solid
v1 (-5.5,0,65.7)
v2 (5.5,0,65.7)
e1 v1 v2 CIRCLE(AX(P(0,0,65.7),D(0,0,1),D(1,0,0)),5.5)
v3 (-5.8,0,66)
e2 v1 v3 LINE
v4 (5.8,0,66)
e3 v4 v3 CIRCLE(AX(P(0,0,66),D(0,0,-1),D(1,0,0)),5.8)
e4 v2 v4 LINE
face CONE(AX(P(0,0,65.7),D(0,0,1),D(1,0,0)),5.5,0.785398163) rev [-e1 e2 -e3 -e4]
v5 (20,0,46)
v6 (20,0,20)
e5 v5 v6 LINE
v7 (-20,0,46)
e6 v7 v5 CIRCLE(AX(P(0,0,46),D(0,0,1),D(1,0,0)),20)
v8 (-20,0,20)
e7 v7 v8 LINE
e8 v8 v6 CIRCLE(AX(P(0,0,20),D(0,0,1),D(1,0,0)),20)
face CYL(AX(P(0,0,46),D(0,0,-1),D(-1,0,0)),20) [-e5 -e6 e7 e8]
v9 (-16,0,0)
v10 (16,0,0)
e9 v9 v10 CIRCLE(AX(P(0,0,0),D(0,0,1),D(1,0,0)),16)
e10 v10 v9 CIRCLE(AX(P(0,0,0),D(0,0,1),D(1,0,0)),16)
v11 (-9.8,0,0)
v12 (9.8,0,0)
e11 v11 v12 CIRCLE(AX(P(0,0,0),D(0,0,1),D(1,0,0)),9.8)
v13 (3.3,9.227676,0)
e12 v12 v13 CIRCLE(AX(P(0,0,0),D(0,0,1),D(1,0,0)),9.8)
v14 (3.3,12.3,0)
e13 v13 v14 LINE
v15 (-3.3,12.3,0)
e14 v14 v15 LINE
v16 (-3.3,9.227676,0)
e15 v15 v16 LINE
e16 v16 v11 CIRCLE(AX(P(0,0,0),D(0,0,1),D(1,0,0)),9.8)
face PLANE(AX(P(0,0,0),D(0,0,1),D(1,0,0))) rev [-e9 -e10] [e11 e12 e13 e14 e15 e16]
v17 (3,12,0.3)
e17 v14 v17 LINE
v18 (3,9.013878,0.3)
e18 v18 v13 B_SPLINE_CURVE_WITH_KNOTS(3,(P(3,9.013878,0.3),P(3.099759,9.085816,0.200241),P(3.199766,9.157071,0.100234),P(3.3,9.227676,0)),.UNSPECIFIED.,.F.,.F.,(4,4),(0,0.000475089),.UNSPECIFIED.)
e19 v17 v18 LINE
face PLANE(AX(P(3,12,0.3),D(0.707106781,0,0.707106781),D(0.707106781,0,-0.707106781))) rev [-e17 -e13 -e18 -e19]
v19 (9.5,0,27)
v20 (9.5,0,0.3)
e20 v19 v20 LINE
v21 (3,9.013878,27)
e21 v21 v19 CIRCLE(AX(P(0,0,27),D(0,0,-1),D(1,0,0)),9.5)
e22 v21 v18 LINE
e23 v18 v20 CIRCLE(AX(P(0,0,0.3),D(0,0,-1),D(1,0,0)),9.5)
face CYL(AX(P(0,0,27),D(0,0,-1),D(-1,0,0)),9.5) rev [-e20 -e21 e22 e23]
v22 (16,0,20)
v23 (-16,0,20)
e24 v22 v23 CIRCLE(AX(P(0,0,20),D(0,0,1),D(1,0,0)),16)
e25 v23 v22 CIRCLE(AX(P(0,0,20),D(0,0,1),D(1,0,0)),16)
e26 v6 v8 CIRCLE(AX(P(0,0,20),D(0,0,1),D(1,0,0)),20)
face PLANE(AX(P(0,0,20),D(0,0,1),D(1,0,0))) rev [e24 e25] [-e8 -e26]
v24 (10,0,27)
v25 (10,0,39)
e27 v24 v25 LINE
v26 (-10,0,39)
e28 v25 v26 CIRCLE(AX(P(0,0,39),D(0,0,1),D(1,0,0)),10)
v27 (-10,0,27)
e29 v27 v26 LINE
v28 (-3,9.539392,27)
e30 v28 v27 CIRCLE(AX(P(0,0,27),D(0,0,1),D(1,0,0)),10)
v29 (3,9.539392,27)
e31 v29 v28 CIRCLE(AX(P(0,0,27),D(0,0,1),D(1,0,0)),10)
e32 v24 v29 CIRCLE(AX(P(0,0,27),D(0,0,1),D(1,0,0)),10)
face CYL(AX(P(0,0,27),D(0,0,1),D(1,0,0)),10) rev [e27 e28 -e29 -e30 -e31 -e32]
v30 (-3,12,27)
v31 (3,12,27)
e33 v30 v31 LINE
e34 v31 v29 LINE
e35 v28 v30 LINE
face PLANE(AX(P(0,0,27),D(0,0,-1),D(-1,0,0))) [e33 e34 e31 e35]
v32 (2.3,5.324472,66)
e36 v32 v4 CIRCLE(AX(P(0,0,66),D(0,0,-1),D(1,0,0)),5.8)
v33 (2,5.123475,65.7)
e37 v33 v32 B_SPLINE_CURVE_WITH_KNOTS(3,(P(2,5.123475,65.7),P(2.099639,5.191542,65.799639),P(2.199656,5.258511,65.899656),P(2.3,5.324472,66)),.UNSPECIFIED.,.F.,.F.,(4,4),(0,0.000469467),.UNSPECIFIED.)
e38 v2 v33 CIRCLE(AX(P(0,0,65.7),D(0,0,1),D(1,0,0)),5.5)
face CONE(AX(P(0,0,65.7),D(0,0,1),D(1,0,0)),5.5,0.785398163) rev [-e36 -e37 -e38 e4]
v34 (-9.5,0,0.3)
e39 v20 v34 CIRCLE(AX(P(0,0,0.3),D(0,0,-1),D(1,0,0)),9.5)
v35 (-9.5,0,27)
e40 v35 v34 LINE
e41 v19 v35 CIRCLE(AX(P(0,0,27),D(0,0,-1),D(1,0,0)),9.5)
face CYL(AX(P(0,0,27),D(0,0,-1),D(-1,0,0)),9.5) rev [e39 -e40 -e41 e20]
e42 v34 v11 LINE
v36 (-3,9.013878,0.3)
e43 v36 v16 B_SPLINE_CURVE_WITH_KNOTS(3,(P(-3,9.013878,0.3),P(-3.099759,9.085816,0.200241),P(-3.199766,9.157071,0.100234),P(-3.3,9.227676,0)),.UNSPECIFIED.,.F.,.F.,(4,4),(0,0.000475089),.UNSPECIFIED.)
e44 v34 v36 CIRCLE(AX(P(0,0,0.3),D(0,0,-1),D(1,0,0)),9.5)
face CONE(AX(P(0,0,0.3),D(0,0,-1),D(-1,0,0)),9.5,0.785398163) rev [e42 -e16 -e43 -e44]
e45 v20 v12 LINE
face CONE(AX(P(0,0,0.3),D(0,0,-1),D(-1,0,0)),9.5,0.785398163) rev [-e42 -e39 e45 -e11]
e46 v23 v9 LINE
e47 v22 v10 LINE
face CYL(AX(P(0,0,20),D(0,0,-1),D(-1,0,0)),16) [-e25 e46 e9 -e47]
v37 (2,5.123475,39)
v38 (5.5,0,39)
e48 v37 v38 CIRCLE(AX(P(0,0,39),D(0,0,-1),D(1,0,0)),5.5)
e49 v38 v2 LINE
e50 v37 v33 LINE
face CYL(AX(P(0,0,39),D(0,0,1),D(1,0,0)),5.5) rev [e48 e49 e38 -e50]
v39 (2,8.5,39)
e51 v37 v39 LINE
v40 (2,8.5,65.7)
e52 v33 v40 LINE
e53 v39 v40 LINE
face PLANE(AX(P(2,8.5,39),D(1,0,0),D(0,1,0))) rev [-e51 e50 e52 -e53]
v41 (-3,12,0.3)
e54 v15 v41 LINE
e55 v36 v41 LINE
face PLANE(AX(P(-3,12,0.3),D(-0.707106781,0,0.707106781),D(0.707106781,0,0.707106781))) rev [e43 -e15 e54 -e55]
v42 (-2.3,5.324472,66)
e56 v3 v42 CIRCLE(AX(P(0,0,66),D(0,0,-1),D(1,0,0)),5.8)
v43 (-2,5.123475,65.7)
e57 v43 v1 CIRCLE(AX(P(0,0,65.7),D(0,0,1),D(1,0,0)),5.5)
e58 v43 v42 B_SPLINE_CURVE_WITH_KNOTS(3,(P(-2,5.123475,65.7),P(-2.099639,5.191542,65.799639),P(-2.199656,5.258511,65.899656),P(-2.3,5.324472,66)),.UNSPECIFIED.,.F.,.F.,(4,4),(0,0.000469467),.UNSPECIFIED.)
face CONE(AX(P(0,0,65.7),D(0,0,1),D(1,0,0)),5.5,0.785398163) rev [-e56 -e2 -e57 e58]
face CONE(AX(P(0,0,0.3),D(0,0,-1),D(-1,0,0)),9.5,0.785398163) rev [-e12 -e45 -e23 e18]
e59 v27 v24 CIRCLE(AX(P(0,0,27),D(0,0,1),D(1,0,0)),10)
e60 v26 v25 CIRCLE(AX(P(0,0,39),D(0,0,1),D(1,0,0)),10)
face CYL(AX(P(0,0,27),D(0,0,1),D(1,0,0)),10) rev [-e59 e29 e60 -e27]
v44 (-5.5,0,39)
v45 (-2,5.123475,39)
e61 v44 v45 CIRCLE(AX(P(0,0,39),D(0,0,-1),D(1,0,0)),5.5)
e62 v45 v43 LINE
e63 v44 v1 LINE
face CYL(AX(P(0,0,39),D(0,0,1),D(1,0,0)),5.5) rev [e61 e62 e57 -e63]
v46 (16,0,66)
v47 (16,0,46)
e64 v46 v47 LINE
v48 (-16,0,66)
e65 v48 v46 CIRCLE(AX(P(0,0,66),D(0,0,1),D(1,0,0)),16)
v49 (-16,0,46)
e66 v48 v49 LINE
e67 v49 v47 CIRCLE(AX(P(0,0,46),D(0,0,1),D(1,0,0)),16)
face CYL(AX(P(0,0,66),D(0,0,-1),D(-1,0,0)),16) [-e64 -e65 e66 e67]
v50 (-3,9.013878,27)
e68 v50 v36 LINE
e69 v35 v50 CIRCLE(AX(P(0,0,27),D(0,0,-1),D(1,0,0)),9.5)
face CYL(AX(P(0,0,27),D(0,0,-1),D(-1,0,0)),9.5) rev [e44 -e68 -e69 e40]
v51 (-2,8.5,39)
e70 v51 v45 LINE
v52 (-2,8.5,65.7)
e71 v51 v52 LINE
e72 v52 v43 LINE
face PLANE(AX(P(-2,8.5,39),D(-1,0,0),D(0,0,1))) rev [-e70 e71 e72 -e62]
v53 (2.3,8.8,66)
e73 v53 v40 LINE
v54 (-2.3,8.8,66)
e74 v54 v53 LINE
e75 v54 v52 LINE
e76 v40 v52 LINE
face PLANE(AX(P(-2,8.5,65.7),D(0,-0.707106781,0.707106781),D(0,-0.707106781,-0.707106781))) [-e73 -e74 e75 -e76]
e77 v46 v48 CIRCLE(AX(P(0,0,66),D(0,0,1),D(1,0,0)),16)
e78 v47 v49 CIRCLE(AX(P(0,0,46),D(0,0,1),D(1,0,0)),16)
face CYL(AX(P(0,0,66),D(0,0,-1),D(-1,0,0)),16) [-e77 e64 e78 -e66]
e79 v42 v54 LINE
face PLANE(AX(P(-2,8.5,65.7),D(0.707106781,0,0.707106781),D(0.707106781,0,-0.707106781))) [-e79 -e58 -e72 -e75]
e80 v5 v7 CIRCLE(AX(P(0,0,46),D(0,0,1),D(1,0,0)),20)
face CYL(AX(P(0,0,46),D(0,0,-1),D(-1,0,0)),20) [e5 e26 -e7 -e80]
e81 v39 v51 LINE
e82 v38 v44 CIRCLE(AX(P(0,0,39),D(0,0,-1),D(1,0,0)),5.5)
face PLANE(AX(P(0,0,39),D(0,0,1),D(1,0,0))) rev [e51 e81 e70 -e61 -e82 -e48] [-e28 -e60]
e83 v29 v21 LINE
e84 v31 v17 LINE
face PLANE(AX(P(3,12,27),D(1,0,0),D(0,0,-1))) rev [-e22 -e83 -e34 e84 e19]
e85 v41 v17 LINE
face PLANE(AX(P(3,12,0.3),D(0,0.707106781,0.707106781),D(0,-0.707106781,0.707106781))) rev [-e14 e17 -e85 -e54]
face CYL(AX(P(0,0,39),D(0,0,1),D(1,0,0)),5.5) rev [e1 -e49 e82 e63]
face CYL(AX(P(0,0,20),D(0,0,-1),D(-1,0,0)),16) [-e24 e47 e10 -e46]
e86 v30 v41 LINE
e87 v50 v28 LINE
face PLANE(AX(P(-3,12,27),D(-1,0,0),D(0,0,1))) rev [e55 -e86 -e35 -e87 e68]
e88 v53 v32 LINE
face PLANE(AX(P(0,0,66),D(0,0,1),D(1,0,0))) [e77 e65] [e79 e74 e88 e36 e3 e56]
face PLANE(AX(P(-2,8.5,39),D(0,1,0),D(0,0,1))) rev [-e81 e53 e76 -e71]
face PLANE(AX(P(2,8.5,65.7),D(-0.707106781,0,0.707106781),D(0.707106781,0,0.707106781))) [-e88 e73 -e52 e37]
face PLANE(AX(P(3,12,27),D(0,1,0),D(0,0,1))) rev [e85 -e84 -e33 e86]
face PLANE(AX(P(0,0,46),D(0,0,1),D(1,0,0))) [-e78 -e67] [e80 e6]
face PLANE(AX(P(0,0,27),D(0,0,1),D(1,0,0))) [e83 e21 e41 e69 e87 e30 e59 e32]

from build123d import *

# Parameters (mm, degrees)
SKETCH_1_R          = 16
EXTRUDE_1_DEPTH     = 20
SKETCH_2_R          = 20
EXTRUDE_2_DEPTH     = 26
SKETCH_3_R          = 16
EXTRUDE_3_DEPTH     = 20
SKETCH_4_R          = 9.5
CUT_EXTRUDE_1_DEPTH = 27
SKETCH_5_R          = 5.5
CUT_EXTRUDE_2_DEPTH = 27
SKETCH_6_R          = 10
CUT_EXTRUDE_3_DEPTH = 12
CUT_EXTRUDE_4_DEPTH = 27
CUT_EXTRUDE_5_DEPTH = 27
CHAMFER_1_SIZE      = 0.3


with BuildPart() as part:
    # 草图1 → 拉伸1 (new body)
    with BuildSketch(Plane(origin=(0, 0, 0), x_dir=(0, -1, 0), z_dir=(0, 0, 1))):
        with Locations(Location((0, 0, 0), (0, 0, 90))):
            Circle(SKETCH_1_R)
    extrude(amount=EXTRUDE_1_DEPTH)

    # 草图2 → 拉伸2 (add)
    with BuildSketch(Plane(origin=(0, 0, 20), x_dir=(0, 1, 0), z_dir=(0, 0, 1))):
        with Locations(Location((0, 0, 0), (0, 0, 90))):
            Circle(SKETCH_2_R)
    extrude(amount=EXTRUDE_2_DEPTH)

    # 草图3 → 拉伸3 (add)
    with BuildSketch(Plane(origin=(0, 0, 46), x_dir=(0, 1, 0), z_dir=(0, 0, 1))):
        with Locations(Location((0, 0, 0), (0, 0, 270))):
            Circle(SKETCH_3_R)
    extrude(amount=EXTRUDE_3_DEPTH)

    # 草图4 → 切除-拉伸1 (cut)
    with BuildSketch(Plane(origin=(0, 0, 0), x_dir=(-1, 0, 0), z_dir=(0, 0, -1))):
        Circle(SKETCH_4_R)
    extrude(amount=-CUT_EXTRUDE_1_DEPTH, mode=Mode.SUBTRACT)

    # 草图5 → 切除-拉伸2 (cut)
    with BuildSketch(Plane.XY.offset(66)):
        Circle(SKETCH_5_R)
    extrude(amount=-CUT_EXTRUDE_2_DEPTH, mode=Mode.SUBTRACT)

    # 草图6 → 切除-拉伸3 (cut)
    with BuildSketch(Plane.XY.offset(39)):
        Circle(SKETCH_6_R)
    extrude(amount=-CUT_EXTRUDE_3_DEPTH, mode=Mode.SUBTRACT)

    # 草图7 → 切除-拉伸4 (cut)
    with BuildSketch(Plane(origin=(0, 0, 0), x_dir=(-1, 0, 0), z_dir=(0, 0, -1))):
        with BuildLine():
            Line((-3, 12), (-3, 9.013878189))
            ThreePointArc((-3, 9.013878189), (0, 9.5), (3, 9.013878189))
            Line((3, 9.013878189), (3, 12))
            Line((3, 12), (-3, 12))
        make_face()
    extrude(amount=-CUT_EXTRUDE_4_DEPTH, mode=Mode.SUBTRACT)

    # 草图8 → 切除-拉伸5 (cut)
    with BuildSketch(Plane.XY.offset(66)):
        with BuildLine():
            Line((-2, 8.5), (-2, 5.123475383))
            ThreePointArc((-2, 5.123475383), (0, 5.5), (2, 5.123475383))
            Line((2, 5.123475383), (2, 8.5))
            Line((2, 8.5), (-2, 8.5))
        make_face()
    extrude(amount=-CUT_EXTRUDE_5_DEPTH, mode=Mode.SUBTRACT)

    # 倒角1
    chamfer_1_edges = [part.edges().sort_by_distance(p)[0] for p in [
        (0, -9.5, 0),
        (0, 12, 0),
        (3, 10.506939094, 0),
        (-3, 10.506939094, 0),
        (0, -5.5, 66),
        (0, 8.5, 66),
        (-2, 6.811737691, 66),
        (2, 6.811737691, 66),
    ]]
    chamfer(chamfer_1_edges, length=CHAMFER_1_SIZE)


solid = part.part
